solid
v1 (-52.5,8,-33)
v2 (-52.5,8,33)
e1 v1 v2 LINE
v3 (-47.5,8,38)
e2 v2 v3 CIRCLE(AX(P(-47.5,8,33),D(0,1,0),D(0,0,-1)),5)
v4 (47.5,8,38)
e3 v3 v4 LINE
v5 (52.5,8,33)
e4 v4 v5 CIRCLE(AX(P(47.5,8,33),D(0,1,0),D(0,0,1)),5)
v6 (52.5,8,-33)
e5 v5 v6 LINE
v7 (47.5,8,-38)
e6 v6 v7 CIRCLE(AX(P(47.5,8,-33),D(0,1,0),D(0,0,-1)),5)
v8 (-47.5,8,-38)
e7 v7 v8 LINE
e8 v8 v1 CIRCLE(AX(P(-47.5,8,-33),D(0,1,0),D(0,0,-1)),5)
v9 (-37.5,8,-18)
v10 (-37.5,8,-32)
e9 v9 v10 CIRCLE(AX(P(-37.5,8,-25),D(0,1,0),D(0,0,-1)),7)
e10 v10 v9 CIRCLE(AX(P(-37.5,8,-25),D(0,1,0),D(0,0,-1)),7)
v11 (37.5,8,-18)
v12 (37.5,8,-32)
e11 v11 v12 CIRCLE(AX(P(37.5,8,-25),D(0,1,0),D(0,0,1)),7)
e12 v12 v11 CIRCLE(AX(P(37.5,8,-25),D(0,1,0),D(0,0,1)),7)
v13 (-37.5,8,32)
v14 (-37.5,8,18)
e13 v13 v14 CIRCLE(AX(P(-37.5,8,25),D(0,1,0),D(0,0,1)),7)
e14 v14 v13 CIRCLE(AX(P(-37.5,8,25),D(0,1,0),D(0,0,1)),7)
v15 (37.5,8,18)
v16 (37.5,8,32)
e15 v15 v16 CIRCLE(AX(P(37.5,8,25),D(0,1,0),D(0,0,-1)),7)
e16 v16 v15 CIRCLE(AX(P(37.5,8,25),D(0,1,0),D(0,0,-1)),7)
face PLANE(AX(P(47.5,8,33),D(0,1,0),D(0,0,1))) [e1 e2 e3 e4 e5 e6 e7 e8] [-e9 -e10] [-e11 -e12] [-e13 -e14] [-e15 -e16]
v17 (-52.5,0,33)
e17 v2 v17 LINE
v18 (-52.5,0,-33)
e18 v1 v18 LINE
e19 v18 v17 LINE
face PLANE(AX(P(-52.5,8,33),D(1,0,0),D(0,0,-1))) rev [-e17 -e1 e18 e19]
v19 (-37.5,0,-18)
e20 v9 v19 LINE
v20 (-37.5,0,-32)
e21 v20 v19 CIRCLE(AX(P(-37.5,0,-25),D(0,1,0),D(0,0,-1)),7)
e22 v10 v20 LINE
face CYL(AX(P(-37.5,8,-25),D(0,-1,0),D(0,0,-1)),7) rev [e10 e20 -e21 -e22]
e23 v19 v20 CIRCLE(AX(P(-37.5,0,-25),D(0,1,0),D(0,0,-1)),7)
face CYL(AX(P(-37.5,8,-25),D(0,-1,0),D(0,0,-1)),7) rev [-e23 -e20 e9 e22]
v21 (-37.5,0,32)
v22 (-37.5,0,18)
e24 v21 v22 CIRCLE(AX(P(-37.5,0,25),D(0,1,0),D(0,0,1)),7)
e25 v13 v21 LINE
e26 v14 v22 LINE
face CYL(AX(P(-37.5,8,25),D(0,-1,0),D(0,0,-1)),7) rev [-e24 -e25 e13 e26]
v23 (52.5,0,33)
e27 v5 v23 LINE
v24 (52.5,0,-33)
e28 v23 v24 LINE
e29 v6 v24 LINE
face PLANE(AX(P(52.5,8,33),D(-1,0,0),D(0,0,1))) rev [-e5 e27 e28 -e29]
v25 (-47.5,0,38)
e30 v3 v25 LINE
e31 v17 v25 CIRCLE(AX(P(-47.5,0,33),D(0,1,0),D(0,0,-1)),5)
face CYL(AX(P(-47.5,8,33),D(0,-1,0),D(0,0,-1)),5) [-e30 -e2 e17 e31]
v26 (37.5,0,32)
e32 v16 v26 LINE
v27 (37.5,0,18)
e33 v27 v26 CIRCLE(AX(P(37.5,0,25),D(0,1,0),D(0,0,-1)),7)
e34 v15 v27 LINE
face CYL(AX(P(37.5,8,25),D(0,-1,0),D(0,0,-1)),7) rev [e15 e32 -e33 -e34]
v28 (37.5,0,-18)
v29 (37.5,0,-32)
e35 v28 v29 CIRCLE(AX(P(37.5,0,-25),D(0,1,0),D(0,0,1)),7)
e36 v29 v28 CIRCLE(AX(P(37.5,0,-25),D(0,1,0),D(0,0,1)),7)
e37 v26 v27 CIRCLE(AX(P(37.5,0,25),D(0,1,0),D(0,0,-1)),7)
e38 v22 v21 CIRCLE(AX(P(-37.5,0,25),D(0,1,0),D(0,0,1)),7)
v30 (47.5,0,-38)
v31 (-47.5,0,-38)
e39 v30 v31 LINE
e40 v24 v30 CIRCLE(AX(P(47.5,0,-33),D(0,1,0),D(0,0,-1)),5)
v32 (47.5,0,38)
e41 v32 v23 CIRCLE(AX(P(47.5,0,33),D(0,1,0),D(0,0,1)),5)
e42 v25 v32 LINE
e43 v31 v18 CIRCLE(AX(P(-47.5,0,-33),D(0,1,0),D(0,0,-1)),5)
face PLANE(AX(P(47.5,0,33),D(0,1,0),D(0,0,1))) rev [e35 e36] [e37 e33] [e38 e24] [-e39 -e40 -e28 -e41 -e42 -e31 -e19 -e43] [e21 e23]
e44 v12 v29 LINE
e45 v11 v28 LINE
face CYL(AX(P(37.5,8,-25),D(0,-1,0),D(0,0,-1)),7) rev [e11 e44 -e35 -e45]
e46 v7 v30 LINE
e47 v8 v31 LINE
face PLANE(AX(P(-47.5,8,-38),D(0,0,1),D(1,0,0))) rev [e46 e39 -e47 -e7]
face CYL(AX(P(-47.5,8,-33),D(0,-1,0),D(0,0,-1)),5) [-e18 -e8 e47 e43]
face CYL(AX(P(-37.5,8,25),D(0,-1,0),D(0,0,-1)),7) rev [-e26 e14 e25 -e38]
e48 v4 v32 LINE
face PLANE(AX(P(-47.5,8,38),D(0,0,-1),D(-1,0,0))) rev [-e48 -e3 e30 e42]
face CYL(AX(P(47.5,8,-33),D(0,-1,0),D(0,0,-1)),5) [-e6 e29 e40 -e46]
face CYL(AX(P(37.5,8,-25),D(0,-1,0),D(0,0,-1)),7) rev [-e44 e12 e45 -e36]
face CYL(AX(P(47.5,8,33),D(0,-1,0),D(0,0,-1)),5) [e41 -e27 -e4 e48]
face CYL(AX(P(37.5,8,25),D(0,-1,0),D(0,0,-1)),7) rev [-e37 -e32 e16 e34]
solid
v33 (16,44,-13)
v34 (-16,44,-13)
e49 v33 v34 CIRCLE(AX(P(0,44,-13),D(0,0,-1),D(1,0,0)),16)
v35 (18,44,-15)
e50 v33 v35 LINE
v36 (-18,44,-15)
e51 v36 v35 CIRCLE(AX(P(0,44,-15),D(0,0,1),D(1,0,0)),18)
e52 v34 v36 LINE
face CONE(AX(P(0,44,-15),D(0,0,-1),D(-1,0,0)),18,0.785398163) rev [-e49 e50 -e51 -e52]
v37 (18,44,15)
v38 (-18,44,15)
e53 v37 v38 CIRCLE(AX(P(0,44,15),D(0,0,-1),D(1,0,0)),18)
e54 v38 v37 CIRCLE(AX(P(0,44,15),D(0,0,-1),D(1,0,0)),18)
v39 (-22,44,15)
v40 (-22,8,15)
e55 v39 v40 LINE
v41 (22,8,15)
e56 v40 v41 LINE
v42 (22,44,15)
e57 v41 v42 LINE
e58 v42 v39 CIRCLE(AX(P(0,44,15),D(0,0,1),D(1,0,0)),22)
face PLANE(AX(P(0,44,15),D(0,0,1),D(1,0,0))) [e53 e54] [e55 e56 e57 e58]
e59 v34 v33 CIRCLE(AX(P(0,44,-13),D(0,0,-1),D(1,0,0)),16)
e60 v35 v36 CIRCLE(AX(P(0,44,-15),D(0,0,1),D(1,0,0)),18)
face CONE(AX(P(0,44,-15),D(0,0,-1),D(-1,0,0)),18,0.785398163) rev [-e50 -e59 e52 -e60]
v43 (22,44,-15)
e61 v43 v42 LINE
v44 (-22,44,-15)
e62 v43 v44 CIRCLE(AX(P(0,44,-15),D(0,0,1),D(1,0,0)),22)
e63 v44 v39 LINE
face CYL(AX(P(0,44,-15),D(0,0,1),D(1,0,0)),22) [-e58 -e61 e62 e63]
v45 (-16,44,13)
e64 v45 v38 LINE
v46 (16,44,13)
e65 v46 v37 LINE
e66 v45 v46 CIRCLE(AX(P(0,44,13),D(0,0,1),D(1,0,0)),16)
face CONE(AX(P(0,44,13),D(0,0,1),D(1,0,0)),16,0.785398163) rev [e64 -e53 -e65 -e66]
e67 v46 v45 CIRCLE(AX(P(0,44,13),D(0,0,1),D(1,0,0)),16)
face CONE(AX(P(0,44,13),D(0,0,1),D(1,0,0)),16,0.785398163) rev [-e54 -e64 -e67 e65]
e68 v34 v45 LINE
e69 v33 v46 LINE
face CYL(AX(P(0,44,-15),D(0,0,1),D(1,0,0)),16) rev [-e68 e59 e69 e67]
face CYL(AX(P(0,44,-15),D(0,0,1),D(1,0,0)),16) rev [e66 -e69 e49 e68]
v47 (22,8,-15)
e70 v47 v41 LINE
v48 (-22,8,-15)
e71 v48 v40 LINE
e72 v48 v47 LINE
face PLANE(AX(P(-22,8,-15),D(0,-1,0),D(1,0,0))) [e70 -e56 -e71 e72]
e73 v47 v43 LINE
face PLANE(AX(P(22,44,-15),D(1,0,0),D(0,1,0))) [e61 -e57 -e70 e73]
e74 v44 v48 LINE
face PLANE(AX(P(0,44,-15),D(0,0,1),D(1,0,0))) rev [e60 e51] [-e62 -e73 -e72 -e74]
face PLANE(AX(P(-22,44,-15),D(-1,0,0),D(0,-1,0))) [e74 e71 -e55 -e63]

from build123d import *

# Parameters (mm, degrees)
SKETCH_1_R      = 7
EXTRUDE_1_DEPTH = 8
SKETCH_2_R      = 16
EXTRUDE_2_DEPTH = 15
CHAMFER_1_SIZE  = 2


with BuildPart() as part:
    # 草图1 → 凸台-拉伸1 (new body)
    with BuildSketch(Plane(origin=(0, 0, 0), x_dir=(1, 0, 0), z_dir=(0, 1, 0))):
        with BuildLine():
            Line((-47.5, -38), (47.5, -38))
            ThreePointArc((47.5, -38), (51.035533906, -36.535533906), (52.5, -33))
            Line((52.5, -33), (52.5, 33))
            ThreePointArc((52.5, 33), (51.035533906, 36.535533906), (47.5, 38))
            Line((47.5, 38), (-47.5, 38))
            ThreePointArc((-47.5, 38), (-51.035533906, 36.535533906), (-52.5, 33))
            Line((-52.5, 33), (-52.5, -33))
            ThreePointArc((-52.5, -33), (-51.035533906, -36.535533906), (-47.5, -38))
        make_face()
        with Locations(Location((-37.5, -25, 0), (0, 0, 270))):
            Circle(SKETCH_1_R, mode=Mode.SUBTRACT)
        with Locations(Location((37.5, -25, 0), (0, 0, 90))):
            Circle(SKETCH_1_R, mode=Mode.SUBTRACT)
        with Locations(Location((-37.5, 25, 0), (0, 0, 90))):
            Circle(SKETCH_1_R, mode=Mode.SUBTRACT)
        with Locations(Location((37.5, 25, 0), (0, 0, 270))):
            Circle(SKETCH_1_R, mode=Mode.SUBTRACT)
    extrude(amount=EXTRUDE_1_DEPTH)


with BuildPart() as body_2:
    # 草图2 → 凸台-拉伸2 (new, symmetric)
    with BuildSketch(Plane.XY):
        with BuildLine():
            Line((-22, 44), (-22, 8))
            Line((-22, 8), (22, 8))
            Line((22, 8), (22, 44))
            ThreePointArc((22, 44), (0, 66), (-22, 44))
        make_face()
        with Locations((0, 44)):
            Circle(SKETCH_2_R, mode=Mode.SUBTRACT)
    extrude(amount=EXTRUDE_2_DEPTH, both=True)

    # 倒角1
    chamfer_1_edges = [body_2.edges().sort_by_distance(p)[0] for p in [
        (-16, 44, -15),
        (-16, 44, 15),
    ]]
    chamfer(chamfer_1_edges, length=CHAMFER_1_SIZE)


solid = Compound([part.part, body_2.part])
